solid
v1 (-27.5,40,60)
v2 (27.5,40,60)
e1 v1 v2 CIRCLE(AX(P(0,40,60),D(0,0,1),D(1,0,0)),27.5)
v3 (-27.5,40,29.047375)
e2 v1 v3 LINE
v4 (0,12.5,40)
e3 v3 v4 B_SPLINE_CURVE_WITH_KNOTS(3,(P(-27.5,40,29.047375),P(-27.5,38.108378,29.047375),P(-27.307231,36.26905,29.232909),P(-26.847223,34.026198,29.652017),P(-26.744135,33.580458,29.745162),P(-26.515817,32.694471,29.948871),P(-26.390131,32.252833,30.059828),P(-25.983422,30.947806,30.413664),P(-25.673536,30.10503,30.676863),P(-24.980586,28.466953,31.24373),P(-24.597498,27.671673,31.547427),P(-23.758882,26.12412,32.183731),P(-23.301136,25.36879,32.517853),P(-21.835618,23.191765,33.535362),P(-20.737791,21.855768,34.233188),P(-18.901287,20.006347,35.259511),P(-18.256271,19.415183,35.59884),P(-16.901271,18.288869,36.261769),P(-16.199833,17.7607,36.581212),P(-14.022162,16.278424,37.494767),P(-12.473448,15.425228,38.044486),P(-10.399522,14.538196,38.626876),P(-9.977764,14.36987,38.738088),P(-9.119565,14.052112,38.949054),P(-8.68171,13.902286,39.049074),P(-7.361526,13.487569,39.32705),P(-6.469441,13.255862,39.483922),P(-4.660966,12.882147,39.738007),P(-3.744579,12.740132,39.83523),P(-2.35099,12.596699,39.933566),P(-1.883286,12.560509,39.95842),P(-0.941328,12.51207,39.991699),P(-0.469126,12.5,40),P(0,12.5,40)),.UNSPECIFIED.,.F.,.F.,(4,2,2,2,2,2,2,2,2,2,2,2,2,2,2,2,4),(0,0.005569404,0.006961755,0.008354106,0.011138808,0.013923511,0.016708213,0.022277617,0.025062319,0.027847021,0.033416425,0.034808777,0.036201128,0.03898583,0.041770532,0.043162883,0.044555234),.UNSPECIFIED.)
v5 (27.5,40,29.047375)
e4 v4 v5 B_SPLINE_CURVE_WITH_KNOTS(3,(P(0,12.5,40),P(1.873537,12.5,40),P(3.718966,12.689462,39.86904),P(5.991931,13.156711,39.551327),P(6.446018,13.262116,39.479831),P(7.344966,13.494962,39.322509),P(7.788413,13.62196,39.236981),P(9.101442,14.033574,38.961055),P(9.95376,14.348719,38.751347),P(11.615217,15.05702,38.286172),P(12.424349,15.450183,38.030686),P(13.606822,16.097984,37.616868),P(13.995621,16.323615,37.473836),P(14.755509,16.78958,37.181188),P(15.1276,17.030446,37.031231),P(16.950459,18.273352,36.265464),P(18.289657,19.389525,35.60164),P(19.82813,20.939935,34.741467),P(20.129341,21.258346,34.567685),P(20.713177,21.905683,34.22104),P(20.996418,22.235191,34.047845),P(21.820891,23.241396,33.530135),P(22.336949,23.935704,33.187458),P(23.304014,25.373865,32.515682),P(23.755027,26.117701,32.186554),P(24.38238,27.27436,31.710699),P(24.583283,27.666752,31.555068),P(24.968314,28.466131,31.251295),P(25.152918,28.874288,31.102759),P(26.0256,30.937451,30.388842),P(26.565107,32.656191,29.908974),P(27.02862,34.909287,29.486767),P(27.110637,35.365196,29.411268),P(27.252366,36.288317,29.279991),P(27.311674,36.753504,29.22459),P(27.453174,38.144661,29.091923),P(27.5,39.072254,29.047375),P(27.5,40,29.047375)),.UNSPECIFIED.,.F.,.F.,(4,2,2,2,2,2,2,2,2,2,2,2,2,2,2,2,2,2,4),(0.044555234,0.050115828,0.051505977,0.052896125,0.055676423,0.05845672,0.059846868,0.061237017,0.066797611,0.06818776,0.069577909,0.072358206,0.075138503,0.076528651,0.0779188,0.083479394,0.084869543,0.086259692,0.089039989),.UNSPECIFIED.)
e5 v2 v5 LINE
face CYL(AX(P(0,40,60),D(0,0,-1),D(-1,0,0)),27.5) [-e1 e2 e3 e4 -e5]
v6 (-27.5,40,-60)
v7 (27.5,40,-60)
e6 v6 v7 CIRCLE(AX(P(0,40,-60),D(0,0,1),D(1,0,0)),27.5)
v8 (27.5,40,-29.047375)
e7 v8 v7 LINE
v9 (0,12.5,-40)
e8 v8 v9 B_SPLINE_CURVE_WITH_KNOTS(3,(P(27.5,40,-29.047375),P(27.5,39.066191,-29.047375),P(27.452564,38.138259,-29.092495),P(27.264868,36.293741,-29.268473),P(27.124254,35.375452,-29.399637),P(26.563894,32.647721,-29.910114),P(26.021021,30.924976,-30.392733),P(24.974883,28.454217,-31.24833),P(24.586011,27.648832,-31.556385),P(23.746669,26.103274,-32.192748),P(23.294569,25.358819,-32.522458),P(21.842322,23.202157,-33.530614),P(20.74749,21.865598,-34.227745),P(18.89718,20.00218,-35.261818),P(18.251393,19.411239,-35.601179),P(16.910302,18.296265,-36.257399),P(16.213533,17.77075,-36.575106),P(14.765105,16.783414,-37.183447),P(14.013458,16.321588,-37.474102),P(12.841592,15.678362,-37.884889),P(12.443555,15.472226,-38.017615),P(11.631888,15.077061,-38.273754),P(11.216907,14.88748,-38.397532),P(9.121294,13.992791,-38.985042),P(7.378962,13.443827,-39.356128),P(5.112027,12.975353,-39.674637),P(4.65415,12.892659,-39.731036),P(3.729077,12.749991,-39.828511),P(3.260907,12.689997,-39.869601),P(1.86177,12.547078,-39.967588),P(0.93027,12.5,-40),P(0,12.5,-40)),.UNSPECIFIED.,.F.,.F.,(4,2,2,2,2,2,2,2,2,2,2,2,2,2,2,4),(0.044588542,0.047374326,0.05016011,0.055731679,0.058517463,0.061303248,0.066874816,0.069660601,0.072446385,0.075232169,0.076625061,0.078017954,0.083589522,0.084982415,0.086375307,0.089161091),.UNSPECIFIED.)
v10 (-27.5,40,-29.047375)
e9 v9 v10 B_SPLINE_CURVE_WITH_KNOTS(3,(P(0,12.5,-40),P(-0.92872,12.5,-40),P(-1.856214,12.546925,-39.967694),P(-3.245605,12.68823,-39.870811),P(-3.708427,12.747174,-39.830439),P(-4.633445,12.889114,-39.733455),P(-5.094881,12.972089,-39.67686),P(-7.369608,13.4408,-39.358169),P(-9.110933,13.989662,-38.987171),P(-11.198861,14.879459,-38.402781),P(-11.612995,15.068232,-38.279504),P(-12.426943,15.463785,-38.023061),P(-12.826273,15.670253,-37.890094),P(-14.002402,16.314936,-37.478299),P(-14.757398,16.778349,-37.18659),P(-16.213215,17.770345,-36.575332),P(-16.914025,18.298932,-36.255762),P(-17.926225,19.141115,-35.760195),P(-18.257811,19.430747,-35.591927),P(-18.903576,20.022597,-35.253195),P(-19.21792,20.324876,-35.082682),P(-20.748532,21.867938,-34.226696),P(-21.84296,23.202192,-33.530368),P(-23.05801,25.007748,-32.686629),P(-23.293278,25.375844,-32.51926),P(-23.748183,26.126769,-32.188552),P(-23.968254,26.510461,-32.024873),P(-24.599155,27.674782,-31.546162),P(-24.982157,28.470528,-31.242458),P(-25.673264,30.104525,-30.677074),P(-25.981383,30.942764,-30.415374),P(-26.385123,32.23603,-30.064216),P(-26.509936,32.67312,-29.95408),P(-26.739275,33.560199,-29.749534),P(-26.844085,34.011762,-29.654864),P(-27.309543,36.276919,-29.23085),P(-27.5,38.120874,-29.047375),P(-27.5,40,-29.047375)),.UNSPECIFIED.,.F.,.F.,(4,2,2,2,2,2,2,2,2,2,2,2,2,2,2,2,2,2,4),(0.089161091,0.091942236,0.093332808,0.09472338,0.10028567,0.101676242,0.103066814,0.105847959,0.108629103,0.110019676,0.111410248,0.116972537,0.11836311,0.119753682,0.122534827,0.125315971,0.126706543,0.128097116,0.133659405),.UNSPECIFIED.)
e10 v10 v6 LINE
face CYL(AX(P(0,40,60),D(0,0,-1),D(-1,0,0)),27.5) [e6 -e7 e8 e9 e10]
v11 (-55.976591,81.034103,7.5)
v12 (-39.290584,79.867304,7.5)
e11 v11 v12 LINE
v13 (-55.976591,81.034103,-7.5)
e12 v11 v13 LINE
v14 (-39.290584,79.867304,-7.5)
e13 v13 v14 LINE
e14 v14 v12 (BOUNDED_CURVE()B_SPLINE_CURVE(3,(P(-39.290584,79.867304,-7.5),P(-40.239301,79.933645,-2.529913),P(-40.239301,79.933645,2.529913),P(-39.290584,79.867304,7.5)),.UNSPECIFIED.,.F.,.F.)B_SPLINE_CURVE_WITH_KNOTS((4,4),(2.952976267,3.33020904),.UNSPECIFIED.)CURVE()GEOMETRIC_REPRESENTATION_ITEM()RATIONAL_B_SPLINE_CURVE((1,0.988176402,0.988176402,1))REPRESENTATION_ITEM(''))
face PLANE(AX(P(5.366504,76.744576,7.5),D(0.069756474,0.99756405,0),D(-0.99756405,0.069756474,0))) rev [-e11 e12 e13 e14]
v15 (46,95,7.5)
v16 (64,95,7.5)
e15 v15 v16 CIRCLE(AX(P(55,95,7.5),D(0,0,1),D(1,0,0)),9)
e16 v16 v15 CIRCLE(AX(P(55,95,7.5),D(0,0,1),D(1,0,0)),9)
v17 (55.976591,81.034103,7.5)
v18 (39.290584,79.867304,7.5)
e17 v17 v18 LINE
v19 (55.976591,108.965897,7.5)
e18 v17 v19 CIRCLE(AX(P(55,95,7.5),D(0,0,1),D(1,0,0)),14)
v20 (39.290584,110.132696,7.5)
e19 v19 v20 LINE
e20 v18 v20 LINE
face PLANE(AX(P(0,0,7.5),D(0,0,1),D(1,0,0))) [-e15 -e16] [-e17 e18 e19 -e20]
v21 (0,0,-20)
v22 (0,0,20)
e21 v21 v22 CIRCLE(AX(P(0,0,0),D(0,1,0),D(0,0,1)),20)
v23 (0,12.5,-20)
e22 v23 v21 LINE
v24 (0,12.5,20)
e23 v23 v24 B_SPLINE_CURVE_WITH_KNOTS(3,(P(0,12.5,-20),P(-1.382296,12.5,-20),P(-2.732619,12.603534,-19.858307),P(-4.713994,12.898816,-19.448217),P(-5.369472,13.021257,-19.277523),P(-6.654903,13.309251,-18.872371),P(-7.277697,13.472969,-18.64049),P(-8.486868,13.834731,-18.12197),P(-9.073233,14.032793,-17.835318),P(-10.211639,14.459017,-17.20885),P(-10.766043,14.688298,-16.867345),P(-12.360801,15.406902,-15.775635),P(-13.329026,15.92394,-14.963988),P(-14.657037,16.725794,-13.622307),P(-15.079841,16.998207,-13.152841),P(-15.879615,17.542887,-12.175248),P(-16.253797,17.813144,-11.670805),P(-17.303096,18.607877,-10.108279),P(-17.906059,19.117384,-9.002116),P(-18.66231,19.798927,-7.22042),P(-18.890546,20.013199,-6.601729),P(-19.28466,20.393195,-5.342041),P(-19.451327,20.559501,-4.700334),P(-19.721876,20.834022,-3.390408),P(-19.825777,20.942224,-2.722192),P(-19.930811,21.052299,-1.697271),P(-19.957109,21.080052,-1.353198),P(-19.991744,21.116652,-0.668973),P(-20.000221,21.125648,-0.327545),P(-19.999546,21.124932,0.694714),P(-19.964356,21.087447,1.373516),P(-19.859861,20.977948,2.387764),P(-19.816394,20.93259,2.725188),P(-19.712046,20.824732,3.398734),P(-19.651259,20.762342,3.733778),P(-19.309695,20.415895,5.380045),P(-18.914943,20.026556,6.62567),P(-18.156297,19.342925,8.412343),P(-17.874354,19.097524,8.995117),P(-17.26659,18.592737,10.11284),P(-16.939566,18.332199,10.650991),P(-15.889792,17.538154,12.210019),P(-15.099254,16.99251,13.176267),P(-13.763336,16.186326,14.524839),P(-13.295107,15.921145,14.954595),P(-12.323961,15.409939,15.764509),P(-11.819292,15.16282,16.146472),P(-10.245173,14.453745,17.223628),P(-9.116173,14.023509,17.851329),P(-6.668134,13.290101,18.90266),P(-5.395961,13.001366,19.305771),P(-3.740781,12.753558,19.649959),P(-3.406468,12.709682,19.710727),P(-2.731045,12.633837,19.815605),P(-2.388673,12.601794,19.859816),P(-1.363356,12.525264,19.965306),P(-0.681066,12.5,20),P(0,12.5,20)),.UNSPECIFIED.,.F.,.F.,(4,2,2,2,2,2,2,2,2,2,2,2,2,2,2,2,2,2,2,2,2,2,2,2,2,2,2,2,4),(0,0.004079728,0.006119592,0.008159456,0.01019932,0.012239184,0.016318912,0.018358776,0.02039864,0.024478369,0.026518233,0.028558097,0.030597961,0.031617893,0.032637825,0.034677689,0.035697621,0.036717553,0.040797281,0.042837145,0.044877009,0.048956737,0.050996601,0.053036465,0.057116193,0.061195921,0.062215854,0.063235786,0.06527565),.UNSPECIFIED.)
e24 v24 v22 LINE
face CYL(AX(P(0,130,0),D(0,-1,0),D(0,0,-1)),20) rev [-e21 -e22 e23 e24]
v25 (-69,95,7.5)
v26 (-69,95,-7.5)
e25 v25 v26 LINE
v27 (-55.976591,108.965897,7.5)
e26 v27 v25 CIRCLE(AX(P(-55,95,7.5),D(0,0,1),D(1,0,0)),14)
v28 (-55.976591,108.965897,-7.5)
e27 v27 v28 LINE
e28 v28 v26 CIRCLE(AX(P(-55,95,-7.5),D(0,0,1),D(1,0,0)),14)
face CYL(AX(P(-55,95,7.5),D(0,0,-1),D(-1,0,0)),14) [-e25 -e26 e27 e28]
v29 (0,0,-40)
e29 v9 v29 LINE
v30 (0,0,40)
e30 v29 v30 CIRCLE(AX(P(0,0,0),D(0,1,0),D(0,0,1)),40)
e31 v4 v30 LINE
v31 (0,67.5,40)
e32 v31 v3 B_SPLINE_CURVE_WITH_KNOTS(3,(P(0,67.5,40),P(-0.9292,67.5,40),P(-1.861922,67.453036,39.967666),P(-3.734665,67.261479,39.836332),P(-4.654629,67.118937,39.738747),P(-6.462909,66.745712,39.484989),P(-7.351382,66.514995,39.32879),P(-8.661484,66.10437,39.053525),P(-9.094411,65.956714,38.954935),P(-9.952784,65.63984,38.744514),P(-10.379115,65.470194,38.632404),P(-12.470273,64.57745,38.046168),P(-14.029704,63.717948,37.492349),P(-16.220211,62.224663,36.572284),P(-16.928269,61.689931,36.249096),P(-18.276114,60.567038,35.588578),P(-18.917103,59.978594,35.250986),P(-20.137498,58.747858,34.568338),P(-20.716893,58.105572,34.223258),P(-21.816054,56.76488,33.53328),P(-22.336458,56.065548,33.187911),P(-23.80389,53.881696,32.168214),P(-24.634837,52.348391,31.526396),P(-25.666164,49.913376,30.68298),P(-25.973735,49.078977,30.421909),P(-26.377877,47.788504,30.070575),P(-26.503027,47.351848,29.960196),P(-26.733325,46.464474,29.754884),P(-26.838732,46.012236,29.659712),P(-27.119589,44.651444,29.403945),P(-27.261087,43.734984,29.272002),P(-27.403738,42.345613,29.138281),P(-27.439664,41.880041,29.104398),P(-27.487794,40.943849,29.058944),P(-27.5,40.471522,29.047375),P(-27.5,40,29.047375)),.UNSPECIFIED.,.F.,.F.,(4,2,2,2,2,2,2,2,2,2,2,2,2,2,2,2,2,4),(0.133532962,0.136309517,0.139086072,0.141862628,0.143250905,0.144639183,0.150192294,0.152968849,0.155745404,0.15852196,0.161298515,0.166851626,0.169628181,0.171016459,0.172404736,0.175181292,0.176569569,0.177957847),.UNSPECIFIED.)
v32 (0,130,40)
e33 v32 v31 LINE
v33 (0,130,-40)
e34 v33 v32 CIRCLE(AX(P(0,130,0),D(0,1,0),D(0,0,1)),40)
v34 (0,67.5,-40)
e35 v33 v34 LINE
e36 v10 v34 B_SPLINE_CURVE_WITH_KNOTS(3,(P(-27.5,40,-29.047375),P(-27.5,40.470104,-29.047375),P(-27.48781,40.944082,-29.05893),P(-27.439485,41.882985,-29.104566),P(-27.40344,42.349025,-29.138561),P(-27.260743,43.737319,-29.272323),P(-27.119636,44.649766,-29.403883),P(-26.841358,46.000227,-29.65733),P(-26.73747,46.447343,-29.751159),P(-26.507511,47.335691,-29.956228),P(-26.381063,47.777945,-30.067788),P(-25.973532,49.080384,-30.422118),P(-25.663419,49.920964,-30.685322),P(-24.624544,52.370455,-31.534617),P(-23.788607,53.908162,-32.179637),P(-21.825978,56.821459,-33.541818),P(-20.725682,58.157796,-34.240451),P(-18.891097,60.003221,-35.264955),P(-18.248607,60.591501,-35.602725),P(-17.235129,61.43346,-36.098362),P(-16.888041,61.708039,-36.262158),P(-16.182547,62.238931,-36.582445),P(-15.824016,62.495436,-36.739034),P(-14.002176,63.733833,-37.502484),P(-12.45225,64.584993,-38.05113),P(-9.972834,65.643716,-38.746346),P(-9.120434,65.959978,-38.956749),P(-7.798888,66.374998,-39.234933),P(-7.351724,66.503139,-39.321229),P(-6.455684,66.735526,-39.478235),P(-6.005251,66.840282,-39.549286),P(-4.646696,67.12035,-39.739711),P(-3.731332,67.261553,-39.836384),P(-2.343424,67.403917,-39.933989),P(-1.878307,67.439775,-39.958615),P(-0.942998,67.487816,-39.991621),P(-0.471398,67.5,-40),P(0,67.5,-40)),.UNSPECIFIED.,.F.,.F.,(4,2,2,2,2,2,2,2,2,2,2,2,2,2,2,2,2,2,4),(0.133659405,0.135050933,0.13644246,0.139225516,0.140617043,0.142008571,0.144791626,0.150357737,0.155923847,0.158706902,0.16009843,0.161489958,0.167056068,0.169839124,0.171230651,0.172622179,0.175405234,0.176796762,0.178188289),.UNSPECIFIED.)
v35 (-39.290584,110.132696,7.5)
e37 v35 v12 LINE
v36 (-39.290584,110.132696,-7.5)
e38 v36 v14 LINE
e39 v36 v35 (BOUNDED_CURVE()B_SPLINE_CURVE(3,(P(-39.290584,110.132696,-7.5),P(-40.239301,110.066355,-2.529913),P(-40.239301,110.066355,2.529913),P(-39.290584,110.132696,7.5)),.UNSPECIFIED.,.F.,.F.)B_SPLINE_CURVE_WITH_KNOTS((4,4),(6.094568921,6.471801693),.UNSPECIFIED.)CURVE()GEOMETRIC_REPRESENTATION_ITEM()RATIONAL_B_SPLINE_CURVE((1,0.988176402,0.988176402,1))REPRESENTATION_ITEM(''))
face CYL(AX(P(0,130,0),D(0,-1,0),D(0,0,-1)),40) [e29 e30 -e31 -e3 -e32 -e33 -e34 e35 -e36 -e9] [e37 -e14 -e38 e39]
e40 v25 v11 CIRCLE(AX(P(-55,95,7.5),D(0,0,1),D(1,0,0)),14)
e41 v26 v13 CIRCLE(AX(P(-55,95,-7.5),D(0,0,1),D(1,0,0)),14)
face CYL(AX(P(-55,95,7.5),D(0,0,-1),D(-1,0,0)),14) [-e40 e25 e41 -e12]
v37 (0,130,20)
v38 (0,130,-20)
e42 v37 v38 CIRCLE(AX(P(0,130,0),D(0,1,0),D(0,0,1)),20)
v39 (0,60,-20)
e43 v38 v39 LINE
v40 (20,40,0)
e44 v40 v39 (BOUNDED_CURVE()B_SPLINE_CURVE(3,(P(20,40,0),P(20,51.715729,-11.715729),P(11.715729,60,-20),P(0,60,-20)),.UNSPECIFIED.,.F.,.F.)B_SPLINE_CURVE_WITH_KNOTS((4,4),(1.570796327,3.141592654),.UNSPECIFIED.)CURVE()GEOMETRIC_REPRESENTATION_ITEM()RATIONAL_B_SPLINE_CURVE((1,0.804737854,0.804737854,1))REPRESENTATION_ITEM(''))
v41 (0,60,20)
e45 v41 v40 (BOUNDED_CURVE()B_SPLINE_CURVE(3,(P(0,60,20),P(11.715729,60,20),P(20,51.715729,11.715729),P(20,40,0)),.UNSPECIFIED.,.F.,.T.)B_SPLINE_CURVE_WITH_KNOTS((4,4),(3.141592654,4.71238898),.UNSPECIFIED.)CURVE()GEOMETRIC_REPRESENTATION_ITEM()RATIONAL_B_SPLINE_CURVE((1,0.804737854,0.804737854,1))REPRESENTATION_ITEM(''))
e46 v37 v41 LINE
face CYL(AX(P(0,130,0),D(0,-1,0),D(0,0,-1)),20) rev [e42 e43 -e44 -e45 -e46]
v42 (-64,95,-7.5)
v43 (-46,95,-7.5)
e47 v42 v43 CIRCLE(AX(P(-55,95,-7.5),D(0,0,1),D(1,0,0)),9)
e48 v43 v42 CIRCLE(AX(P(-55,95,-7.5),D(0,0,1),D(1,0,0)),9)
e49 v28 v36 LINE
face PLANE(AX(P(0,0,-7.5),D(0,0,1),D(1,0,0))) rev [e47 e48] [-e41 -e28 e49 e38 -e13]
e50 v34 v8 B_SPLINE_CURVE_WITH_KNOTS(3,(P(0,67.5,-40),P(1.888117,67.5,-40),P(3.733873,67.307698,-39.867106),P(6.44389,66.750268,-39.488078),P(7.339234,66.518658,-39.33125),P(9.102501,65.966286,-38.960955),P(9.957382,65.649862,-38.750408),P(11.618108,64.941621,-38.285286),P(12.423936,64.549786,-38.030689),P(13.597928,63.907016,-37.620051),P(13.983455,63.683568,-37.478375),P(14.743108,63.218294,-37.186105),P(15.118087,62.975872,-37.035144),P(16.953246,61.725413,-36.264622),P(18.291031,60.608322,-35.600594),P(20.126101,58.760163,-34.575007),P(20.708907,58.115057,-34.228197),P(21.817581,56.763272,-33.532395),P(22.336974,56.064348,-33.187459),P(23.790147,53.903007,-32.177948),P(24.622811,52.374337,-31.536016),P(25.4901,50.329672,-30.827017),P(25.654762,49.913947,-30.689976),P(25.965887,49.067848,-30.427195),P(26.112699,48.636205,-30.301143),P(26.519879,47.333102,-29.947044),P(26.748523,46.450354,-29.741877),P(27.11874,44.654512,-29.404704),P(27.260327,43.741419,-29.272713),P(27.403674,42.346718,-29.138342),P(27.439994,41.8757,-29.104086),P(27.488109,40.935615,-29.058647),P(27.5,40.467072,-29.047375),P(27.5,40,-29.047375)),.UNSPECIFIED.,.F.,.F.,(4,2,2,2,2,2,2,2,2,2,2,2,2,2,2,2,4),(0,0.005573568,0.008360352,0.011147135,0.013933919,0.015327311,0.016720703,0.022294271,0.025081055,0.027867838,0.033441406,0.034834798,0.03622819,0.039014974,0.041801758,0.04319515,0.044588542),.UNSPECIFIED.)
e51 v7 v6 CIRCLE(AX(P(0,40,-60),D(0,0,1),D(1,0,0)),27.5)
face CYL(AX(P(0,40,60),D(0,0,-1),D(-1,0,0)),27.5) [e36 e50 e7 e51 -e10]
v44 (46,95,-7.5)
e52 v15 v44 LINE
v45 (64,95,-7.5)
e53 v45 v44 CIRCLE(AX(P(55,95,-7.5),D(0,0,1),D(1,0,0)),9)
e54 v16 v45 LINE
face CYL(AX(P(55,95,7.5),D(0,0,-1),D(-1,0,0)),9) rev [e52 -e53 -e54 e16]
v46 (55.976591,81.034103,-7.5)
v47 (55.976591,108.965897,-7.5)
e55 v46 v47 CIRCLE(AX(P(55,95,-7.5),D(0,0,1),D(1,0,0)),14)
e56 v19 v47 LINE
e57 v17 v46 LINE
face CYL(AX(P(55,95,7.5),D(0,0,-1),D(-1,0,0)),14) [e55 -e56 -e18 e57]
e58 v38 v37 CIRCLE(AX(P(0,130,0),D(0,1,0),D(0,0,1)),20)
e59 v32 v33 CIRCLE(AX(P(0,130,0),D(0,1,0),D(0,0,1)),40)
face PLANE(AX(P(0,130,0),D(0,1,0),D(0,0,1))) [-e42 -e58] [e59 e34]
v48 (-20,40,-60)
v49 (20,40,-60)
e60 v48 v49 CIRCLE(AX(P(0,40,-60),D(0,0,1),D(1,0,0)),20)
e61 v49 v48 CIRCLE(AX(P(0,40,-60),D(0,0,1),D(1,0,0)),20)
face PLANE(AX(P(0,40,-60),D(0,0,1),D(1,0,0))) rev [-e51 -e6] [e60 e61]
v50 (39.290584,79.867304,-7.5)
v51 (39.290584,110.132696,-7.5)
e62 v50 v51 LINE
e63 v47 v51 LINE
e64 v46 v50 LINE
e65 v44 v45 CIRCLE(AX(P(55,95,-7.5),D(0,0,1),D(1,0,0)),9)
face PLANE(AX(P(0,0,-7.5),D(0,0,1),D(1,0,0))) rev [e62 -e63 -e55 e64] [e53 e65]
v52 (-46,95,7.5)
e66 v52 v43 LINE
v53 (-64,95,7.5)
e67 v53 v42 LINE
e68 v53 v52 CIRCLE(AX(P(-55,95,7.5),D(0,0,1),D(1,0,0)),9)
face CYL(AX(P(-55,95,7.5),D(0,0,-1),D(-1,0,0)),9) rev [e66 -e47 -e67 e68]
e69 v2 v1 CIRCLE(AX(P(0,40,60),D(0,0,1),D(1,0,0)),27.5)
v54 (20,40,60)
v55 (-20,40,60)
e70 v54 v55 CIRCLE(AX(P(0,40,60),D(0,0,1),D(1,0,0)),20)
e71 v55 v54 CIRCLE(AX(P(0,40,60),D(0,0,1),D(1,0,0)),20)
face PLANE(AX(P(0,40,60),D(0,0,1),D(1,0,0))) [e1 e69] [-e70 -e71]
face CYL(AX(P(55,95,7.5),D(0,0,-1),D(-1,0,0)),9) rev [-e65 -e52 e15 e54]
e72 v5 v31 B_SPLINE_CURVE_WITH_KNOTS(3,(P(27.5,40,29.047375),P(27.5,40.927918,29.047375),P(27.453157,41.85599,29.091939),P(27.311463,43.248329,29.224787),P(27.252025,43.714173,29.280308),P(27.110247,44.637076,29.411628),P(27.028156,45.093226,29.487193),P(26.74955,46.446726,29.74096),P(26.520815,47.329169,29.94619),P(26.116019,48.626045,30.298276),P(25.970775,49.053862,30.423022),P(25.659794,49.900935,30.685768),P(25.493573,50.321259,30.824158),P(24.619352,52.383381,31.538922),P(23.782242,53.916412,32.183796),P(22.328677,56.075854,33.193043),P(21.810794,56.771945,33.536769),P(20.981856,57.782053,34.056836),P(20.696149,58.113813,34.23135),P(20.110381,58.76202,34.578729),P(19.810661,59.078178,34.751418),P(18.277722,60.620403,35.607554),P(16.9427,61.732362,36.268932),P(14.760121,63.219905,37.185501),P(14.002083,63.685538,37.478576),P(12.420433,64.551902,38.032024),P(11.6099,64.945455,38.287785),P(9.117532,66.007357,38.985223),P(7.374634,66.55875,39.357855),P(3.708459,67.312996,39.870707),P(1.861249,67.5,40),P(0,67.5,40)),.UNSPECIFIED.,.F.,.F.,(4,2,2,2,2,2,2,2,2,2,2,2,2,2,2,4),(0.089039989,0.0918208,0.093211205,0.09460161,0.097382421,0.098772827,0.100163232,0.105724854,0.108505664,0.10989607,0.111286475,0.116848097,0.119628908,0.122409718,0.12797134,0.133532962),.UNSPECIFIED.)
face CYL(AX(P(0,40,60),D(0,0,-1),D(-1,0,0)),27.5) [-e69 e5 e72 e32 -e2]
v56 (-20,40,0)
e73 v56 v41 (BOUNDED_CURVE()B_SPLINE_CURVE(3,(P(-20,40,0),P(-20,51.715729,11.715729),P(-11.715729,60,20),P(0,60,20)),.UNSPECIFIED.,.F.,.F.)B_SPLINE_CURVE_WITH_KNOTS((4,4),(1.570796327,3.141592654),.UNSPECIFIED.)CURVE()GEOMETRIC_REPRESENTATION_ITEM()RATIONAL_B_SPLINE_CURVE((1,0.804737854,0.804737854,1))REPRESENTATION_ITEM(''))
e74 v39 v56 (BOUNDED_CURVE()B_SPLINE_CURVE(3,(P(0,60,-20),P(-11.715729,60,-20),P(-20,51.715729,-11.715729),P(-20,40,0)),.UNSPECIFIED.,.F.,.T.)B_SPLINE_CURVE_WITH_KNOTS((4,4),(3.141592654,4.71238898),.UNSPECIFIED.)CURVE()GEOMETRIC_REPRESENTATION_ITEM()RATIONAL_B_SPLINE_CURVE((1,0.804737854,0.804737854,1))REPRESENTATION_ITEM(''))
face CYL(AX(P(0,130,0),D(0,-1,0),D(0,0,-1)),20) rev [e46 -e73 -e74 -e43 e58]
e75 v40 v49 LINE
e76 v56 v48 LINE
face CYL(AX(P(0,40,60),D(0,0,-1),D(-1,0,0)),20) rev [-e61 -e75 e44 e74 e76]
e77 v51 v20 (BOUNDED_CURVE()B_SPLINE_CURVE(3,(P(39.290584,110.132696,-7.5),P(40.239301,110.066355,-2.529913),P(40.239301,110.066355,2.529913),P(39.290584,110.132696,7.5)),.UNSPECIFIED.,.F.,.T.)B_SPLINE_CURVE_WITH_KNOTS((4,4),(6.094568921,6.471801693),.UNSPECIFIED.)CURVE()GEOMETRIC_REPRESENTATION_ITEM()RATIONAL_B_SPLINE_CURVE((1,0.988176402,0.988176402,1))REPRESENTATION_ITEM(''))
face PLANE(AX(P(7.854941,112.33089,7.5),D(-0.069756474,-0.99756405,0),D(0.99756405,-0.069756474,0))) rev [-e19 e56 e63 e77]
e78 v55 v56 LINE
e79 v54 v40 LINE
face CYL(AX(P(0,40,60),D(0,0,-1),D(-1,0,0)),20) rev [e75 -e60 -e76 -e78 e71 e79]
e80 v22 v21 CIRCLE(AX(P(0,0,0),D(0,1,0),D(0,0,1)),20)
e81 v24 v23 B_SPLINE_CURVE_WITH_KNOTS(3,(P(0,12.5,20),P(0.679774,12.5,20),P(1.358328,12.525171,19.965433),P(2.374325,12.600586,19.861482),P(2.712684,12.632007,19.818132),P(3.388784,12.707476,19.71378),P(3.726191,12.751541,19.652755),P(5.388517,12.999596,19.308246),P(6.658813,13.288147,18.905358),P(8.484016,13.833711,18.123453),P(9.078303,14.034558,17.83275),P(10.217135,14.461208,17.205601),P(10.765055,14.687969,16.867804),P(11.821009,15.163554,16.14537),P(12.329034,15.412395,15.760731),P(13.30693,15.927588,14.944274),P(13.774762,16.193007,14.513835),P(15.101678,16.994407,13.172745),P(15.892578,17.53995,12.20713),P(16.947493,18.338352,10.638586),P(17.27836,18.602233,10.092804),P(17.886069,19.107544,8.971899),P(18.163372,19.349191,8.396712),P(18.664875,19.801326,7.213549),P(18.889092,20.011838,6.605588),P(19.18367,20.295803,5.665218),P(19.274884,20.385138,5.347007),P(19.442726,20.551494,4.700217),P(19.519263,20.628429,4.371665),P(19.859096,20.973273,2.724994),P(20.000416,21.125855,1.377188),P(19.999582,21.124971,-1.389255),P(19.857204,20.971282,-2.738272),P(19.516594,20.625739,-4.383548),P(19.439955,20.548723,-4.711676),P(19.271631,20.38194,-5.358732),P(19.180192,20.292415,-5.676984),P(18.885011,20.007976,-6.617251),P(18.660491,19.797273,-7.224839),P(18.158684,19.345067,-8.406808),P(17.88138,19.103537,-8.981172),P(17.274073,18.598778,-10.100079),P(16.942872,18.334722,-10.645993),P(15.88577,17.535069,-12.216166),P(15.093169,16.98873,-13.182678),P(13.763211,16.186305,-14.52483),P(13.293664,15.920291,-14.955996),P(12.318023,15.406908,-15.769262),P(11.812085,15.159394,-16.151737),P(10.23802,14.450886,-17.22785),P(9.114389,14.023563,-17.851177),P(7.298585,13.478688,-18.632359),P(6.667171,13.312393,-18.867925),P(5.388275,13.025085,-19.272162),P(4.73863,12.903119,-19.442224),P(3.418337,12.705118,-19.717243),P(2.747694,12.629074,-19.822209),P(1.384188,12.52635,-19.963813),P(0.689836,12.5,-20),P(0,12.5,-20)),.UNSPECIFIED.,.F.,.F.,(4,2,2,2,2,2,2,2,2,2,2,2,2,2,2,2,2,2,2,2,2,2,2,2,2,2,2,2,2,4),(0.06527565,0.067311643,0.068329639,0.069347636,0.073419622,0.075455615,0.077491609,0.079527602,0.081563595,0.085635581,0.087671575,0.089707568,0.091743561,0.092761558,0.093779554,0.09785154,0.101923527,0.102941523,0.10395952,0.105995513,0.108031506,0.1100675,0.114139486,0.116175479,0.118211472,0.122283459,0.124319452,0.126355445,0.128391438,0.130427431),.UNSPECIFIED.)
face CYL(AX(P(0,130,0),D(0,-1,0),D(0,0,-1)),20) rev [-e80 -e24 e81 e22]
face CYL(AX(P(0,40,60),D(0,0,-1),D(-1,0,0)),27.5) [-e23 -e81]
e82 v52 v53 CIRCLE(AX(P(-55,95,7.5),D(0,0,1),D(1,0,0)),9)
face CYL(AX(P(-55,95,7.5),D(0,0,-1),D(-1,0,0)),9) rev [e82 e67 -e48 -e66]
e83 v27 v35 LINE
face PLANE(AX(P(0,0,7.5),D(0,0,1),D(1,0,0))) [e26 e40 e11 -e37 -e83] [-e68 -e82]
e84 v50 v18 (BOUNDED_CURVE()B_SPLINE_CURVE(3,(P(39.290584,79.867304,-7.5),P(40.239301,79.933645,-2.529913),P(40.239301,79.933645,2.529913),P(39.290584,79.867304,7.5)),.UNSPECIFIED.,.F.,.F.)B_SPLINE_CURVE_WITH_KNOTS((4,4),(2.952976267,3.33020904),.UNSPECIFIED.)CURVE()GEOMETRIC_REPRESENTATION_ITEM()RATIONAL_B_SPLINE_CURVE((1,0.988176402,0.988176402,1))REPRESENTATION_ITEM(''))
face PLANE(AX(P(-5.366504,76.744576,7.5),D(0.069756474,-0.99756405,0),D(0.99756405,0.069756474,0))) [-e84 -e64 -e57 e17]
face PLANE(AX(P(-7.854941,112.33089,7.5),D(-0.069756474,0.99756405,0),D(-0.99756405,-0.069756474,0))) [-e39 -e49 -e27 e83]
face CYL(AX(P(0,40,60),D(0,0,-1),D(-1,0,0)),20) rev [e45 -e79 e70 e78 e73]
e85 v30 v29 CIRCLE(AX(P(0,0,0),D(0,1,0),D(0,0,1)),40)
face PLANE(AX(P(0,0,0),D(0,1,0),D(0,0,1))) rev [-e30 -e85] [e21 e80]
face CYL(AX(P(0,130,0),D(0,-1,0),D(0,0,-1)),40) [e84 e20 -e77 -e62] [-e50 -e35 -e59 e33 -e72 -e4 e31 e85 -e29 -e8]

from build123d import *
from build123d.topology import SkipClean

# Parameters (mm, degrees)
MAIN_BODY_SKETCH_R     = 40
MAIN_BODY_SKETCH_R_2   = 20
MAIN_BODY_DEPTH        = 130
CROSS_BOSS_SKETCH_R    = 27.5
CROSS_BOSS_SKETCH_R_2  = 20
CROSS_BOSS_DEPTH       = 60
MOUNTING_LUGS_SKETCH_R = 9
MOUNTING_LUGS_DEPTH    = 7.5
TOP_START              = -90
TOP_BORE_SKETCH_R      = 20
TOP_BORE_DEPTH         = 90
CROSS_START            = -150
CROSS_BORE_SKETCH_R    = 20
CROSS_BORE_DEPTH       = 150


with BuildPart() as part:
    # Main Body Sketch → Main Body (new body)
    with BuildSketch(Plane(origin=(0, 0, 0), x_dir=(1, 0, 0), z_dir=(0, 1, 0))):
        with Locations(Location((0, 0, 0), (0, 0, 270))):
            Circle(MAIN_BODY_SKETCH_R)
        with Locations(Location((0, 0, 0), (0, 0, 270))):
            Circle(MAIN_BODY_SKETCH_R_2, mode=Mode.SUBTRACT)
    extrude(amount=MAIN_BODY_DEPTH)

    # Cross Boss Sketch → Cross Boss (add, symmetric)
    with BuildSketch(Plane.XY):
        with Locations(Location((0, 40, 0), (0, 0, 180))):
            Circle(CROSS_BOSS_SKETCH_R)
        with Locations(Location((0, 40, 0), (0, 0, 180))):
            Circle(CROSS_BOSS_SKETCH_R_2, mode=Mode.SUBTRACT)
    extrude(amount=CROSS_BOSS_DEPTH, both=True)

    # Mounting Lugs Sketch → Mounting Lugs (add, symmetric)
    # profile 1 of 2: a face of its own
    with BuildSketch(Plane.XY):
        with BuildLine():
            Line((-19.924205085, 78.513074912), (0, 78.666038311))
            Line((0, 78.666038311), (0, 111.258543393))
            Line((0, 111.258543393), (-23.164655311, 111.260330734))
            Line((-23.164655311, 111.260330734), (-55.976590632, 108.965896704))
            ThreePointArc((-55.976590632, 108.965896704), (-69, 95), (-55.976590632, 81.034103296))
            Line((-55.976590632, 81.034103296), (-19.924205085, 78.513074912))
        make_face()
        with Locations((-55, 95)):
            Circle(MOUNTING_LUGS_SKETCH_R, mode=Mode.SUBTRACT)
    # profile 2 of 2: a face of its own
    with BuildSketch(Plane.XY):
        with BuildLine():
            Line((0, 111.258543393), (0, 78.666038311))
            Line((0, 78.666038311), (24.838727552, 78.8567318))
            Line((24.838727552, 78.8567318), (55.976590632, 81.034103296))
            ThreePointArc((55.976590632, 81.034103296), (69, 95), (55.976590632, 108.965896704))
            Line((55.976590632, 108.965896704), (23.215832129, 111.256752103))
            Line((23.215832129, 111.256752103), (0, 111.258543393))
        make_face()
        with Locations((55, 95)):
            Circle(MOUNTING_LUGS_SKETCH_R, mode=Mode.SUBTRACT)
    extrude(amount=MOUNTING_LUGS_DEPTH, both=True)

    # Top Bore Sketch → Top Bore (cut)
    with SkipClean():  # the faces are left unmerged after this step: merging them gives an invalid solid
        with BuildSketch(Plane(origin=(0, 130, 0), x_dir=(1, 0, 0), z_dir=(0, 1, 0)).offset(TOP_START)):
            with Locations(Location((0, 0, 0), (0, 0, 180))):
                Circle(TOP_BORE_SKETCH_R)
        extrude(amount=TOP_BORE_DEPTH, mode=Mode.SUBTRACT)

    # Cross Bore Sketch → Cross Bore (cut)
    with SkipClean():  # the faces are left unmerged after this step: merging them gives an invalid solid
        with BuildSketch(Plane.XY.offset(60).offset(CROSS_START)):
            with Locations((0, 40)):
                Circle(CROSS_BORE_SKETCH_R)
        extrude(amount=CROSS_BORE_DEPTH, mode=Mode.SUBTRACT)


solid = part.part
